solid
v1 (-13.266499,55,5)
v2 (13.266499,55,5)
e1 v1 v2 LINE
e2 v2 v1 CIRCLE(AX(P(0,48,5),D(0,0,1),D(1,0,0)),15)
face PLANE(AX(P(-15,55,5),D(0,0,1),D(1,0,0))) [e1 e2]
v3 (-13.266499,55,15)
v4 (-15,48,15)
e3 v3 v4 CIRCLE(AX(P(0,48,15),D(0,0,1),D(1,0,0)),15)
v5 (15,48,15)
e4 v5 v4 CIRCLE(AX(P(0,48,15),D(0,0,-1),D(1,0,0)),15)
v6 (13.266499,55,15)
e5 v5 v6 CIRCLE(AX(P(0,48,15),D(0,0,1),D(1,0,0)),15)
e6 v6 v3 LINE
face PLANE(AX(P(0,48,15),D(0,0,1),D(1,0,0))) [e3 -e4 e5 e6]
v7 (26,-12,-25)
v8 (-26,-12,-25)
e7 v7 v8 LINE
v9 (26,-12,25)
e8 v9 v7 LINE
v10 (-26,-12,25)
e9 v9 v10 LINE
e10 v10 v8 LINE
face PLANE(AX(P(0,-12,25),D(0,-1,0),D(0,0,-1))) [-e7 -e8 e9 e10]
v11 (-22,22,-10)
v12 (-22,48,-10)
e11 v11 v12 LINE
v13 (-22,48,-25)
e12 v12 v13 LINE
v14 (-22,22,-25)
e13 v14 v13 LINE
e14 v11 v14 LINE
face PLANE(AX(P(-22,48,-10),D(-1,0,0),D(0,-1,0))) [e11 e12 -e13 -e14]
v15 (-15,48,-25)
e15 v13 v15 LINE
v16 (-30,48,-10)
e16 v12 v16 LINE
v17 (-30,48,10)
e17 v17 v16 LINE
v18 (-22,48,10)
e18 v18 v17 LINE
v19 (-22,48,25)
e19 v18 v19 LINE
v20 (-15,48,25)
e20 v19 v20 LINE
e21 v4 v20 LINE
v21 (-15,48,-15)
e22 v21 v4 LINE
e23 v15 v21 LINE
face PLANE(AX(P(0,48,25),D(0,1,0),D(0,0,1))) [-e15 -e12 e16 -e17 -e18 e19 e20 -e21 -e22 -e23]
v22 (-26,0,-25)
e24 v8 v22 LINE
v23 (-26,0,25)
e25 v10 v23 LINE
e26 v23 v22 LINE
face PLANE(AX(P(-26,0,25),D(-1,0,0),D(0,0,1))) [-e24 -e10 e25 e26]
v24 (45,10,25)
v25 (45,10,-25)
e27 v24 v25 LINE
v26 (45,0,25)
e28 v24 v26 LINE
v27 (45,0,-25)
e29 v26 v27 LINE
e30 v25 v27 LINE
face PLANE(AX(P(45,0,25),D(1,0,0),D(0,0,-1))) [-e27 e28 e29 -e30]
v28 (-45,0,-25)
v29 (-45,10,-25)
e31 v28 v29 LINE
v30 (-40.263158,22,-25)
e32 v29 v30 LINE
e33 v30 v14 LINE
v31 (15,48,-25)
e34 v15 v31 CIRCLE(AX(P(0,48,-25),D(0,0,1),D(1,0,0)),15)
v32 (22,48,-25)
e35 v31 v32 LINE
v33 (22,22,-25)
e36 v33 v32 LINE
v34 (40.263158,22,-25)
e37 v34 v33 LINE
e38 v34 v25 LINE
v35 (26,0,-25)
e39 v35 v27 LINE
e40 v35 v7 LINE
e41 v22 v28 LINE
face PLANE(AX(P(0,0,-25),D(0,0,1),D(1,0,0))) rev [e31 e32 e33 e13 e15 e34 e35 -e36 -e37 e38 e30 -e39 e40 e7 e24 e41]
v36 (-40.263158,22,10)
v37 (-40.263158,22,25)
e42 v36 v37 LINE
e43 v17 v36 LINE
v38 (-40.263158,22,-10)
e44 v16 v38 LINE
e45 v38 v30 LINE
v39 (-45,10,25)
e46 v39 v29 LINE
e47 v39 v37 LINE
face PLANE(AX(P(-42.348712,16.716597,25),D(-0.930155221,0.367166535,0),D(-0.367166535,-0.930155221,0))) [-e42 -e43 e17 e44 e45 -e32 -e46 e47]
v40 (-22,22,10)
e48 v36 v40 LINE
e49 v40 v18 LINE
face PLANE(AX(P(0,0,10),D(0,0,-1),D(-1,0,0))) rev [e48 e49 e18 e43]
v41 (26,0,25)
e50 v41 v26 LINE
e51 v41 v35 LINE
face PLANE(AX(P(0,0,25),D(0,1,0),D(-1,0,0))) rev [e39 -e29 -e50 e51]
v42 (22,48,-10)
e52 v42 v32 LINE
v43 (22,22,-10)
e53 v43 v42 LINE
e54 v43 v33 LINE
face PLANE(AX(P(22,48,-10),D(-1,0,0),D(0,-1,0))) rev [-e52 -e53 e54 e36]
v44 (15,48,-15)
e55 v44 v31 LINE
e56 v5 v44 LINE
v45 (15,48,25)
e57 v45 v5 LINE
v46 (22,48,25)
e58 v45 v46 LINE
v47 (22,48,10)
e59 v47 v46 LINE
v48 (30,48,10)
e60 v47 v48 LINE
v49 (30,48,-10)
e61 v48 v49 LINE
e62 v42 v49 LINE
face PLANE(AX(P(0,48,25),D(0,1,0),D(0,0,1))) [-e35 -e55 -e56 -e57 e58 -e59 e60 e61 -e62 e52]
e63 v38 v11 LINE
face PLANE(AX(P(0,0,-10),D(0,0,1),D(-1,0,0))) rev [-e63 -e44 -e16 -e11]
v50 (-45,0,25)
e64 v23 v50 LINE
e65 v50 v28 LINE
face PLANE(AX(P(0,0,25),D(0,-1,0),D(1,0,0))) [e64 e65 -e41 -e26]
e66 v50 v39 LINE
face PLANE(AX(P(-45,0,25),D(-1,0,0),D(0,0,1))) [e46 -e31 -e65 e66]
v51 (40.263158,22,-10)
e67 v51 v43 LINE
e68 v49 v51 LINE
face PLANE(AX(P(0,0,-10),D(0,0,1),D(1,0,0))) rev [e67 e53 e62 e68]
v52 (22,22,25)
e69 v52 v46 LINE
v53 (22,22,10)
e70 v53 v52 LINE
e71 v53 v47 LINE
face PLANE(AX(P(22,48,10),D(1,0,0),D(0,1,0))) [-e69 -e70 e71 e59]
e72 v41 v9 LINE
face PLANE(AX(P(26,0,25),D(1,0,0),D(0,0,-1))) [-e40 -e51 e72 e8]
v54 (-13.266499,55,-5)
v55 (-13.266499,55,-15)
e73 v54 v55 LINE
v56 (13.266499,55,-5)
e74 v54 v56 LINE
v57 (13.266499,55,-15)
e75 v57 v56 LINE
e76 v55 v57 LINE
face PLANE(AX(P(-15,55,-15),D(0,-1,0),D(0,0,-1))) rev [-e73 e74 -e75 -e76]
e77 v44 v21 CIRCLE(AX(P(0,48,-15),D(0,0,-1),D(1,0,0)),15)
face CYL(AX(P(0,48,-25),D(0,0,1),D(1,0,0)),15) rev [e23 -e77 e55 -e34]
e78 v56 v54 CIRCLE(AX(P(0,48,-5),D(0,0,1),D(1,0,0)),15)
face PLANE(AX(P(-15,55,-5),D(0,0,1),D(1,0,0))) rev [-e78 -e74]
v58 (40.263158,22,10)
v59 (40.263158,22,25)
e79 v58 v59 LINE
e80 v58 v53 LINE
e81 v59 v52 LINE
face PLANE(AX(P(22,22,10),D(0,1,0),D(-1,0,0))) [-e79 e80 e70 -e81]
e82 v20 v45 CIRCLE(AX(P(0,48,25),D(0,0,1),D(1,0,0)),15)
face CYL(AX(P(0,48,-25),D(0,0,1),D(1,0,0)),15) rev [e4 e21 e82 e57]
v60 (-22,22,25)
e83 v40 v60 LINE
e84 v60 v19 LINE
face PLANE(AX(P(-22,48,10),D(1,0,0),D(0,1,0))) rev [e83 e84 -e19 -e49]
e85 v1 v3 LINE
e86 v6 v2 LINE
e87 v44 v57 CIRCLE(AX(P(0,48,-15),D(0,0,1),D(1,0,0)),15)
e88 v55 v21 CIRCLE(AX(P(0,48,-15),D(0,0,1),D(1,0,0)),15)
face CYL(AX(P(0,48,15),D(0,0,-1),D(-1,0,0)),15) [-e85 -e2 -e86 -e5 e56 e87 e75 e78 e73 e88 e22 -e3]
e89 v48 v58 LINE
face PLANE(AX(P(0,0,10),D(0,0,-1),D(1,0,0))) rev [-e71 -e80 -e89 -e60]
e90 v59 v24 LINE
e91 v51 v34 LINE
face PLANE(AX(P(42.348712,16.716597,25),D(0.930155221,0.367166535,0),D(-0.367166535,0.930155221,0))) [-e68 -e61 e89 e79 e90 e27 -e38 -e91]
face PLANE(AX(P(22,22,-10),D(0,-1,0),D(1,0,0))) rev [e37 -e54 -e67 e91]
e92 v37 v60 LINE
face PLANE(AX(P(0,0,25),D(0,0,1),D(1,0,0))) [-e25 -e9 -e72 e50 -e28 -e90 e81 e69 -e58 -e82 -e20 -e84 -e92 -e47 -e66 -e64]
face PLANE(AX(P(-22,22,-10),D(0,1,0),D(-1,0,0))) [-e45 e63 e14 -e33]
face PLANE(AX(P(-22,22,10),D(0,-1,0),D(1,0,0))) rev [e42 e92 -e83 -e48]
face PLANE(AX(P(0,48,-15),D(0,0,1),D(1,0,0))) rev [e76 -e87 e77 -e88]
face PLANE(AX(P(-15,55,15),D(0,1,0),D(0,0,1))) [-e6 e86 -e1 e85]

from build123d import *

# Parameters (mm, degrees)
SADDLE_BODY_DEPTH                      = 25
CORNER_POCKET_34X22_DEPTH              = 15
CORNER_POCKET_MIRROR_SIDE_COPY_1_DEPTH = 15
BORE_SKETCH_R                          = 15
BORE_30_DEPTH                          = 83.637763765
BORE_PLUG_SKETCH_R                     = 15
BORE_PLUG_DEPTH                        = 15
PLUG_SLOT_SKETCH_W                     = 10
PLUG_SLOT_SKETCH_H                     = 8
PLUG_SLOT_8X10_DEPTH                   = 15


with BuildPart() as part:
    # Saddle Profile Sketch → Saddle Body (new, symmetric)
    with BuildSketch(Plane.XY):
        Polygon((-45, 0), (-45, 10), (-30, 48), (30, 48), (45, 10), (45, 0), (26, 0), (26, -12), (-26, -12), (-26, 0), align=None)
    extrude(amount=SADDLE_BODY_DEPTH, both=True)

    # Corner Pocket Sketch → Corner Pocket 34x22 (cut)
    with BuildSketch(Plane.XY.offset(25)):
        Polygon((-30, 48), (-22, 48), (-22, 22), (-40.263157895, 22), align=None)
    corner_pocket_34x22 = extrude(amount=-CORNER_POCKET_34X22_DEPTH, mode=Mode.SUBTRACT)

    # Corner Pocket Mirror Front: Corner Pocket 34x22 across plane
    add(corner_pocket_34x22.mirror(Plane.XY), mode=Mode.SUBTRACT)

    # Corner Pocket Mirror Side: Corner Pocket 34x22 across plane
    add(corner_pocket_34x22.mirror(Plane(origin=(0, 0, 0), x_dir=(0, 0, 1), z_dir=(1, 0, 0))), mode=Mode.SUBTRACT)

    # Corner Pocket Mirror Side copy 1 sketch → Corner Pocket Mirror Side copy 1 (cut)
    with BuildSketch(Plane(origin=(0, 0, -25), x_dir=(-1, 0, 0), z_dir=(0, 0, -1))):
        Polygon((-30, 48), (-22, 48), (-22, 22), (-40.263157895, 22), align=None)
    extrude(amount=-CORNER_POCKET_MIRROR_SIDE_COPY_1_DEPTH, mode=Mode.SUBTRACT)

    # Bore Sketch → Bore Ø30 (cut, through all)
    with BuildSketch(Plane.XY.offset(25)):
        with Locations((0, 48)):
            Circle(BORE_SKETCH_R)
    extrude(amount=-BORE_30_DEPTH, mode=Mode.SUBTRACT)

    # Bore Plug Sketch → Bore Plug (add, symmetric)
    with BuildSketch(Plane.XY):
        with Locations((0, 48)):
            Circle(BORE_PLUG_SKETCH_R)
    extrude(amount=BORE_PLUG_DEPTH, both=True)

    # Plug Slot Sketch → Plug Slot 8x10 (cut, symmetric)
    with BuildSketch(Plane(origin=(0, 0, 0), x_dir=(0, 0, -1), z_dir=(1, 0, 0))):
        with Locations((10, 59)):
            Rectangle(PLUG_SLOT_SKETCH_W, PLUG_SLOT_SKETCH_H)
    plug_slot_8x10 = extrude(amount=PLUG_SLOT_8X10_DEPTH, both=True, mode=Mode.SUBTRACT)

    # Plug Slot Mirror: Plug Slot 8x10 across plane
    add(plug_slot_8x10.mirror(Plane.XY), mode=Mode.SUBTRACT)


solid = part.part
